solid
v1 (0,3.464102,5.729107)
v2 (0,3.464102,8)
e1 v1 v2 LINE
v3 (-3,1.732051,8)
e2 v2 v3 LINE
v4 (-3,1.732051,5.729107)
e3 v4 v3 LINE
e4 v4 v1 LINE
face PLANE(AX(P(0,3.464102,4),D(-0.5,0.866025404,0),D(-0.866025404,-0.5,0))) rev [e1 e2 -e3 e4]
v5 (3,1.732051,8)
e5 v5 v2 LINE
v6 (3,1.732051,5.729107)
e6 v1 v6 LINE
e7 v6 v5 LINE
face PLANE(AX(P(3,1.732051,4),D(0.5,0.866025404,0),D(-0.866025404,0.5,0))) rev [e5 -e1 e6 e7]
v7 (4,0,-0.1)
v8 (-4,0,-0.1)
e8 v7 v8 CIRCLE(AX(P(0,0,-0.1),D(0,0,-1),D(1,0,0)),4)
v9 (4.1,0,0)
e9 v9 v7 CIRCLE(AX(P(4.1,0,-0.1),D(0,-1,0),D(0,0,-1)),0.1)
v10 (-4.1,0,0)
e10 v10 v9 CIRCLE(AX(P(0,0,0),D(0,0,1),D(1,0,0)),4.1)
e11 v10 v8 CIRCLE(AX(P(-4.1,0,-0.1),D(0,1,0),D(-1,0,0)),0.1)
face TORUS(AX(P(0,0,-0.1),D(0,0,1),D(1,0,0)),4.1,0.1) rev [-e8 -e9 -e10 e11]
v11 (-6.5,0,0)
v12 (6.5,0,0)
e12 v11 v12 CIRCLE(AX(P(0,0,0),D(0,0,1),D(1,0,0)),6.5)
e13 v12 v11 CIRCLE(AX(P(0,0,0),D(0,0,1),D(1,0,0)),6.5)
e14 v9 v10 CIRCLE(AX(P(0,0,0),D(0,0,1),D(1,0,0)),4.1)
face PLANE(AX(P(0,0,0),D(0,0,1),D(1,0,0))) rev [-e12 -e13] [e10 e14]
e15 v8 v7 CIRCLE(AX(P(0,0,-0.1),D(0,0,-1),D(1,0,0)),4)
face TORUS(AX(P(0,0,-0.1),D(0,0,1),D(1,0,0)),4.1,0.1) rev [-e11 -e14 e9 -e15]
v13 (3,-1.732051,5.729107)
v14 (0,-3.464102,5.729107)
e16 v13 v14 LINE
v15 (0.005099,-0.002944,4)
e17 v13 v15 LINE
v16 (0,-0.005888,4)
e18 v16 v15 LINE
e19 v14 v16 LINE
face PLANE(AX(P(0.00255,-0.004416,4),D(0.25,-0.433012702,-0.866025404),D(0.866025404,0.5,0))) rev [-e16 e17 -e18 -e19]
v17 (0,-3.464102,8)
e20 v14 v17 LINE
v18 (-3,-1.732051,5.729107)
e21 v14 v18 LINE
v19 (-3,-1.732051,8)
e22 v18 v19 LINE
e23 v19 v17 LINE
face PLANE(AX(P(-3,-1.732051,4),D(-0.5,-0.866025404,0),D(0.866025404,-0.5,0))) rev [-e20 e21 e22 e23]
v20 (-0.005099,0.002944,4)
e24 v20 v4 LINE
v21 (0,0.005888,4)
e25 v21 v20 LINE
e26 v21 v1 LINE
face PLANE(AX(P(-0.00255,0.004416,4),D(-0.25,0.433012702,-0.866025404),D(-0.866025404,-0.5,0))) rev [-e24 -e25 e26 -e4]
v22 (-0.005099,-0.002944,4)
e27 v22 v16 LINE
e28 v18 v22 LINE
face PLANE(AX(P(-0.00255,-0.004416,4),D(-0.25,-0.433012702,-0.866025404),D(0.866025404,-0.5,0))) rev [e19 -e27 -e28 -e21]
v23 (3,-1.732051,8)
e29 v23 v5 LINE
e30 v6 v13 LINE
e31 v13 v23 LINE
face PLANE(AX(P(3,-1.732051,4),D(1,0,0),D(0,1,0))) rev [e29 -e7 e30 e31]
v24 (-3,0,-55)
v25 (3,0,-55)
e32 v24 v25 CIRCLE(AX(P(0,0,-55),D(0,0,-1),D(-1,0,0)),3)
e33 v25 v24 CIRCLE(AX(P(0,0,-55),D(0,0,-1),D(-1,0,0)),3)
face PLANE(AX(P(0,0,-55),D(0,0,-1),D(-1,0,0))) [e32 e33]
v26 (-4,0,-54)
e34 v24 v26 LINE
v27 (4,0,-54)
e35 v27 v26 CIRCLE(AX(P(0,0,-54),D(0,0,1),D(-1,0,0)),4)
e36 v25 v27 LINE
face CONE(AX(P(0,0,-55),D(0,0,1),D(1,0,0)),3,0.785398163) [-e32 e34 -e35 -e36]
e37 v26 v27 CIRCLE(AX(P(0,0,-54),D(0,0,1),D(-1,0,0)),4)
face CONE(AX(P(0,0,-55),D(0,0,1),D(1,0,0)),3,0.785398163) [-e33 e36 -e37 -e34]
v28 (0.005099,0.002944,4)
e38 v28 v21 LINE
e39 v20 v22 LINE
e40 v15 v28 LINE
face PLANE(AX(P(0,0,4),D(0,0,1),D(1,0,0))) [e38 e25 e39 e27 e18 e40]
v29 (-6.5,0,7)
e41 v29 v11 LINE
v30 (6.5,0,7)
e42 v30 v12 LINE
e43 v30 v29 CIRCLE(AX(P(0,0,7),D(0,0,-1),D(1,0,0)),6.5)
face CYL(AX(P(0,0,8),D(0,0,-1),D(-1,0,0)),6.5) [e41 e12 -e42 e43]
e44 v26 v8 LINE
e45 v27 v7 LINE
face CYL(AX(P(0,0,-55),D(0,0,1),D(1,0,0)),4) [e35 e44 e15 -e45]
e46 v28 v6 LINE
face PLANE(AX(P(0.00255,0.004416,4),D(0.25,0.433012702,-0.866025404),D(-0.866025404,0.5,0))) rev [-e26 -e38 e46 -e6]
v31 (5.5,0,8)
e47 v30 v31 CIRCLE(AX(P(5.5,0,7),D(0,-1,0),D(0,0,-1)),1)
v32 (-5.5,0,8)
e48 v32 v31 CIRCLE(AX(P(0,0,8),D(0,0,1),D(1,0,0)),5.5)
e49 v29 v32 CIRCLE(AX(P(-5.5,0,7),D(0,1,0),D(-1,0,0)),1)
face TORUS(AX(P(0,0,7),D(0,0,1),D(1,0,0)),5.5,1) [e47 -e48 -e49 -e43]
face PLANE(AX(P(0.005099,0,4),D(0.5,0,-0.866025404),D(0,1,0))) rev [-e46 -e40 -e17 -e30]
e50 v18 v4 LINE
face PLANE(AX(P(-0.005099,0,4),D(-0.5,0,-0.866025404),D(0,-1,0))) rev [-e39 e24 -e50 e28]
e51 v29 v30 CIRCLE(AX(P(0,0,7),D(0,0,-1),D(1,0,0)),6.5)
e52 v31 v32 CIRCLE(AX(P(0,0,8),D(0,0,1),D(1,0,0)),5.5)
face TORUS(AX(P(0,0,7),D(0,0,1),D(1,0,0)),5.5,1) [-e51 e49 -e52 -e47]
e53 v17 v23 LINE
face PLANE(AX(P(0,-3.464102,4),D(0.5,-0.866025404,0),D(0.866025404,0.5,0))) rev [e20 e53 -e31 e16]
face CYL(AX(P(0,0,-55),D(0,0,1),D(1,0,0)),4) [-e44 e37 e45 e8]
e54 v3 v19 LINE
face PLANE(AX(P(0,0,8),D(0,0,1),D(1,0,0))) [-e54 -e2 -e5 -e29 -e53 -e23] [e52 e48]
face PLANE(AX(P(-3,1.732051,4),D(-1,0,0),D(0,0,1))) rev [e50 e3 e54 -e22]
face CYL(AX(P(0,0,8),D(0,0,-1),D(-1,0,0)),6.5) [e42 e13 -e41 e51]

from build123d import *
from OCP.BRepFilletAPI import BRepFilletAPI_MakeChamfer

# Parameters (mm, degrees)
SKETCH1_R           = 6.5
BOSS_EXTRUDE1_DEPTH = 8
CUT_EXTRUDE1_DEPTH  = 4
SKETCH3_R           = 4
BOSS_EXTRUDE2_DEPTH = 55
CHAMFER1_SIZE       = 1
FILLET1_R           = 1
CHAMFER2_SIZE       = 1.729106628
CHAMFER2_SIZE2      = 2.994900532
FILLET2_R           = 0.1


with BuildPart() as part:
    # Sketch1 → Boss-Extrude1 (new body)
    with BuildSketch(Plane.XY):
        Circle(SKETCH1_R)
    extrude(amount=BOSS_EXTRUDE1_DEPTH)

    # Sketch2 → Cut-Extrude1 (cut)
    with BuildSketch(Plane.XY.offset(8)):
        Polygon((3, 1.732050808), (0, 3.464101615), (-3, 1.732050808), (-3, -1.732050808), (0, -3.464101615), (3, -1.732050808), align=None)
    extrude(amount=-CUT_EXTRUDE1_DEPTH, mode=Mode.SUBTRACT)

    # Sketch3 → Boss-Extrude2 (add)
    with BuildSketch(Plane(origin=(0, 0, 0), x_dir=(-1, 0, 0), z_dir=(0, 0, -1))):
        with Locations(Location((0, 0, 0), (0, 0, 180))):
            Circle(SKETCH3_R)
    extrude(amount=BOSS_EXTRUDE2_DEPTH)

    # Chamfer1
    chamfer1_edges = [part.edges().sort_by_distance(p)[0] for p in [
        (-4, 0, -55),
    ]]
    chamfer(chamfer1_edges, length=CHAMFER1_SIZE)

    # Fillet1
    fillet1_edges = [part.edges().sort_by_distance(p)[0] for p in [
        (-6.5, 0, 8),
    ]]
    fillet(fillet1_edges, radius=FILLET1_R)

    # Chamfer2: one chamfer whose edges measure the first distance from different faces: ONE call of the kernel's chamfer builder (chamfer() names one face for all edges)
    chamfer2_edges_1 = [part.edges().sort_by_distance(p)[0] for p in [
        (-1.5, 2.598076211, 4),
    ]]
    chamfer2_side_1 = [part.faces().sort_by_distance(p)[0] for p in [
        (-1.5, 2.598076211, 6),
    ]]
    chamfer2_edges_2 = [part.edges().sort_by_distance(p)[0] for p in [
        (1.5, 2.598076211, 4),
    ]]
    chamfer2_side_2 = [part.faces().sort_by_distance(p)[0] for p in [
        (1.5, 2.598076211, 6),
    ]]
    chamfer2_edges_3 = [part.edges().sort_by_distance(p)[0] for p in [
        (3, 0, 4),
    ]]
    chamfer2_side_3 = [part.faces().sort_by_distance(p)[0] for p in [
        (3, 0, 6),
    ]]
    chamfer2_edges_4 = [part.edges().sort_by_distance(p)[0] for p in [
        (1.5, -2.598076211, 4),
    ]]
    chamfer2_side_4 = [part.faces().sort_by_distance(p)[0] for p in [
        (1.5, -2.598076211, 6),
    ]]
    chamfer2_edges_5 = [part.edges().sort_by_distance(p)[0] for p in [
        (-1.5, -2.598076211, 4),
    ]]
    chamfer2_side_5 = [part.faces().sort_by_distance(p)[0] for p in [
        (-1.5, -2.598076211, 6),
    ]]
    chamfer2_edges_6 = [part.edges().sort_by_distance(p)[0] for p in [
        (-3, 0, 4),
    ]]
    chamfer2_side_6 = [part.faces().sort_by_distance(p)[0] for p in [
        (-3, 0, 6),
    ]]
    chamfer2 = BRepFilletAPI_MakeChamfer(part.part.solid().wrapped)
    for e in chamfer2_edges_1:
        chamfer2.Add(CHAMFER2_SIZE, CHAMFER2_SIZE2, e.wrapped, chamfer2_side_1[0].wrapped)  # the first distance lies on this face
    for e in chamfer2_edges_2:
        chamfer2.Add(CHAMFER2_SIZE, CHAMFER2_SIZE2, e.wrapped, chamfer2_side_2[0].wrapped)  # the first distance lies on this face
    for e in chamfer2_edges_3:
        chamfer2.Add(CHAMFER2_SIZE, CHAMFER2_SIZE2, e.wrapped, chamfer2_side_3[0].wrapped)  # the first distance lies on this face
    for e in chamfer2_edges_4:
        chamfer2.Add(CHAMFER2_SIZE, CHAMFER2_SIZE2, e.wrapped, chamfer2_side_4[0].wrapped)  # the first distance lies on this face
    for e in chamfer2_edges_5:
        chamfer2.Add(CHAMFER2_SIZE, CHAMFER2_SIZE2, e.wrapped, chamfer2_side_5[0].wrapped)  # the first distance lies on this face
    for e in chamfer2_edges_6:
        chamfer2.Add(CHAMFER2_SIZE, CHAMFER2_SIZE2, e.wrapped, chamfer2_side_6[0].wrapped)  # the first distance lies on this face
    add(Compound.cast(chamfer2.Shape()), mode=Mode.REPLACE)

    # Fillet2
    fillet2_edges = [part.edges().sort_by_distance(p)[0] for p in [
        (-4, 0, 0),
    ]]
    fillet(fillet2_edges, radius=FILLET2_R)


solid = part.part
